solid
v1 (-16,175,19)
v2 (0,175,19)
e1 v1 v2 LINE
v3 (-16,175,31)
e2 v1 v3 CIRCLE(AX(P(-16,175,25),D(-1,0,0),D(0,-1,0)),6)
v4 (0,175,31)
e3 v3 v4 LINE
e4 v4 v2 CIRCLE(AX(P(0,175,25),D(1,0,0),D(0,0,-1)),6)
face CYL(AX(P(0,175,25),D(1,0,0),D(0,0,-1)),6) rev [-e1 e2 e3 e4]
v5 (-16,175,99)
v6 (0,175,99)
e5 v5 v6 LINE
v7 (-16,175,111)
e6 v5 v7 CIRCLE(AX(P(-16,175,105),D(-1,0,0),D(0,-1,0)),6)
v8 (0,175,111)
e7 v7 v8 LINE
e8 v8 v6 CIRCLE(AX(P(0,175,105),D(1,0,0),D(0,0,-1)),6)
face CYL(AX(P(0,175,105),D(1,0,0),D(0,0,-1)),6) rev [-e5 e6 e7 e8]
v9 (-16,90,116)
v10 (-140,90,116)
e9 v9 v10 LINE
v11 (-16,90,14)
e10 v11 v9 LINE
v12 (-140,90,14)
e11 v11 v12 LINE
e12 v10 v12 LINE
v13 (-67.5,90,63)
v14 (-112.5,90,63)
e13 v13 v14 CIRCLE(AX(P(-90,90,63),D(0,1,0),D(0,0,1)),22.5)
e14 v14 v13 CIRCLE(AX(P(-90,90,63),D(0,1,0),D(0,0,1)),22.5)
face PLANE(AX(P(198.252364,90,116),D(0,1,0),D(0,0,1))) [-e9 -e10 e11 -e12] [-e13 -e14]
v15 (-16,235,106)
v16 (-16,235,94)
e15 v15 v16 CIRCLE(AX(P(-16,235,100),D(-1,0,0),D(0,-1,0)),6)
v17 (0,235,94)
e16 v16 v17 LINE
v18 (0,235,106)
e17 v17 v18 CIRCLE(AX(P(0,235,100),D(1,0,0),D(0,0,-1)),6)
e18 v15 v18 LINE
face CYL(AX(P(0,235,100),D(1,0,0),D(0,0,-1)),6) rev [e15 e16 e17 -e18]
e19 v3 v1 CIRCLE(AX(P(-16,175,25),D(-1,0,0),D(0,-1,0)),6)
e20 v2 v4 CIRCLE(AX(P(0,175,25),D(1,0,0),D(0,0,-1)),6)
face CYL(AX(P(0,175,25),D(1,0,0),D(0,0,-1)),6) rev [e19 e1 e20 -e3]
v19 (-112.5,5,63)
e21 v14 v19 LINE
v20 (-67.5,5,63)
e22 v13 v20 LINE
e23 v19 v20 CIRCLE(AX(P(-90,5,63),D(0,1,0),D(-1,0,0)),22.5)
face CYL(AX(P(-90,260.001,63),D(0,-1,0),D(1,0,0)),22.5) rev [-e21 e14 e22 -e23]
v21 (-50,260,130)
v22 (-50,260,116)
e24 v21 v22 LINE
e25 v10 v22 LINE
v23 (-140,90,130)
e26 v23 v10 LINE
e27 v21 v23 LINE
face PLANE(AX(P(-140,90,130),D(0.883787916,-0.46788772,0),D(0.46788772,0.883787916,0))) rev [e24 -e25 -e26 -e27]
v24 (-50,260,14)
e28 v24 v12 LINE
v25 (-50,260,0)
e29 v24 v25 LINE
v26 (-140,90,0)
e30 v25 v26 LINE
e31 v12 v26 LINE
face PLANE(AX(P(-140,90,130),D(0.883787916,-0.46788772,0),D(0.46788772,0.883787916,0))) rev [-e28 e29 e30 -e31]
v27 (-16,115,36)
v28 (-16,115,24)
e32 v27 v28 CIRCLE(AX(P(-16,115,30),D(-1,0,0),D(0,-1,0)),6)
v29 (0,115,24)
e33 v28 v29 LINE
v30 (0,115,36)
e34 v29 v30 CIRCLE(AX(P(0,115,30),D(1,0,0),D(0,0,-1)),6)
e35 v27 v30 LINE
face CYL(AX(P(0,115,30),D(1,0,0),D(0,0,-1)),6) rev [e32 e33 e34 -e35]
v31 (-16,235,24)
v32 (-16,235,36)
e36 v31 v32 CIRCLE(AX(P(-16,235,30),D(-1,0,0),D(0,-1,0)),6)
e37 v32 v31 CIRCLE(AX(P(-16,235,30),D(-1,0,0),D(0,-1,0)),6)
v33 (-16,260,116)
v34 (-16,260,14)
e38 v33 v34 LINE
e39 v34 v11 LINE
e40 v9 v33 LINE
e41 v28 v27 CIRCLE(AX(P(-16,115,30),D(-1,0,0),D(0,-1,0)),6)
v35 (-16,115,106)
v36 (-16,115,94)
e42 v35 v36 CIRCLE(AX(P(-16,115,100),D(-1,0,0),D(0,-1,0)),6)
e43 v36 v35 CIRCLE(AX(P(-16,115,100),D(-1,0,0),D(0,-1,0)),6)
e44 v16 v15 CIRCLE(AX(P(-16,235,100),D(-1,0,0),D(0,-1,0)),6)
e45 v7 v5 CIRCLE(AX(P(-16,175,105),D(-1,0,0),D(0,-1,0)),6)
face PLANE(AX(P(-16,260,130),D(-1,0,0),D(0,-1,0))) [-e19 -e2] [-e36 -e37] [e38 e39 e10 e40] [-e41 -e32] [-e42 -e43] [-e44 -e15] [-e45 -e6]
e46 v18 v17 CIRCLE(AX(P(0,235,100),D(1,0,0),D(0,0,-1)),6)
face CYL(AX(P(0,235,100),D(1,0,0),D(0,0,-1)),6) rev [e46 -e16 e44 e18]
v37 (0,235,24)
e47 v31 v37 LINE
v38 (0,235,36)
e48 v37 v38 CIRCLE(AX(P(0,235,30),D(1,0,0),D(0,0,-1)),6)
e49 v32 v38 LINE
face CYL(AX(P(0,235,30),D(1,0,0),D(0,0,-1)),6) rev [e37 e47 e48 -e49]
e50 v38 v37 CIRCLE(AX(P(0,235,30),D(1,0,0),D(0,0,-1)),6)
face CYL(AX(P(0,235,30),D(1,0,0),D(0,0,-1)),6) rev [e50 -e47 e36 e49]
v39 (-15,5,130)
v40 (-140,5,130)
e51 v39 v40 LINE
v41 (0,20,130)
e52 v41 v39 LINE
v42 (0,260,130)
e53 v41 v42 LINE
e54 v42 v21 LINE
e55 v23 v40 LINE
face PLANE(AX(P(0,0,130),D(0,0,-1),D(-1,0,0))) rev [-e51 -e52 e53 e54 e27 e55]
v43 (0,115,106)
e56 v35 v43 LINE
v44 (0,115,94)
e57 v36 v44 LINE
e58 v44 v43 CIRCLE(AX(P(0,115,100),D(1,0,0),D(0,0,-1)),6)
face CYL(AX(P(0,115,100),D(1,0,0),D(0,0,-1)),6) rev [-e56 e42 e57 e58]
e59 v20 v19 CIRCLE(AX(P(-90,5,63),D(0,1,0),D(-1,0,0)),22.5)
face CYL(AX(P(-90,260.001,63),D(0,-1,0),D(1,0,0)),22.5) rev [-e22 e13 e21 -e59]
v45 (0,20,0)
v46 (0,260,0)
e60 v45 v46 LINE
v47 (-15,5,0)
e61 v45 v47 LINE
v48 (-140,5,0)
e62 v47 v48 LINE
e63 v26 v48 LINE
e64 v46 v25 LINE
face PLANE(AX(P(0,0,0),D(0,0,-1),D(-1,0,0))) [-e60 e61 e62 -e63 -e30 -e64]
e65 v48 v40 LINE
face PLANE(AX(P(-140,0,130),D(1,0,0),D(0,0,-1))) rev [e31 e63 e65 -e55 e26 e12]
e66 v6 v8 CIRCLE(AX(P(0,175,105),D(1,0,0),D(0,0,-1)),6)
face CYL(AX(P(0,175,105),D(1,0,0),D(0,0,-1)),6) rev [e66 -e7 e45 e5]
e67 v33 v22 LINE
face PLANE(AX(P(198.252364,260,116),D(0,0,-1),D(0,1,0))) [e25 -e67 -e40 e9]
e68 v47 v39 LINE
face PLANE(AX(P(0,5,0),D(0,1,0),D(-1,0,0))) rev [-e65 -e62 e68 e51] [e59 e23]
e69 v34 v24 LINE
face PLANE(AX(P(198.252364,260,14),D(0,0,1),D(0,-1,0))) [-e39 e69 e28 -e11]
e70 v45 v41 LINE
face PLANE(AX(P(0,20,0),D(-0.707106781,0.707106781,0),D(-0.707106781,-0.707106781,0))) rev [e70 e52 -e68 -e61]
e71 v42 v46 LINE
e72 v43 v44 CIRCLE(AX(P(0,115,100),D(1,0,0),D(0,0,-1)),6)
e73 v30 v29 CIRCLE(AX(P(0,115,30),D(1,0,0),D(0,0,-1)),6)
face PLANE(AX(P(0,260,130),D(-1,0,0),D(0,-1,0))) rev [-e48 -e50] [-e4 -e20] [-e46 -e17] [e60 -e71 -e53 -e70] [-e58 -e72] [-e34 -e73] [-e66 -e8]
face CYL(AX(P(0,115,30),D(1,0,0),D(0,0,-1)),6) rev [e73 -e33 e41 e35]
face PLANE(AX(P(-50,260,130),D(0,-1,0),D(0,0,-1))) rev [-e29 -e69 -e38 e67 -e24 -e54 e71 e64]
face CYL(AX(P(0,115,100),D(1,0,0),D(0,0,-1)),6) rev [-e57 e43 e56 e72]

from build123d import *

# Parameters (mm, degrees)
EXTRUDE_1_DEPTH             = 130
SKETCH_2_W                  = 140
SKETCH_2_H                  = 5
CUT_EXTRUDE_1_DEPTH         = 323.645316098
SKETCH_3_W                  = 102
SKETCH_3_H                  = 170
CUT_EXTRUDE_2_DEPTH         = 124
CUT_EXTRUDE_3_DEPTH         = 323.645316098
HOLE_WIZARD_M14_1_D         = 12
HOLE_WIZARD_M14_1_DEPTH     = 34
HOLE_WIZARD_M14_1_TIP       = 3.605163714
HOLE_WIZARD_12_0_12_1_D     = 12
HOLE_WIZARD_12_0_12_1_DEPTH = 34
HOLE_WIZARD_12_0_12_1_TIP   = 3.605163714
CUT_EXTRUDE_4_REACH         = 302.299
SKETCH_12_R                 = 22.5


with BuildPart() as part:
    # 草图1 → 凸台-拉伸1 (new body)
    with BuildSketch(Plane.XY):
        Polygon((0, 0), (-140, 0), (-140, 90), (-50, 260), (0, 260), align=None)
    extrude(amount=EXTRUDE_1_DEPTH)

    # 草图2 → 切除-拉伸1 (cut, through all)
    with BuildSketch(Plane.XY.offset(130)):
        with Locations((-70, 2.5)):
            Rectangle(SKETCH_2_W, SKETCH_2_H)
    extrude(amount=-CUT_EXTRUDE_1_DEPTH, mode=Mode.SUBTRACT)

    # 草图3 → 切除-拉伸2 (cut)
    with BuildSketch(Plane(origin=(-140, 34.772640959, 0), x_dir=(0, 0, -1), z_dir=(1, 0, 0))):
        with Locations((-65, 140.227359041)):
            Rectangle(SKETCH_3_W, SKETCH_3_H)
    extrude(amount=CUT_EXTRUDE_2_DEPTH, mode=Mode.SUBTRACT)

    # 草图5 → 切除-拉伸3 (cut, through all)
    with BuildSketch(Plane.XY.offset(130)):
        Polygon((0, 5), (0, 20), (-15, 5), align=None)
    extrude(amount=-CUT_EXTRUDE_3_DEPTH, mode=Mode.SUBTRACT)

    # M14 螺纹孔1
    with Locations(Plane(origin=(0, 0, 0), x_dir=(0, 0, -1), z_dir=(1, 0, 0))):
        with Locations((-100, 235), (-30, 235), (-100, 115), (-30, 115)):
            Hole(HOLE_WIZARD_M14_1_D / 2, depth=HOLE_WIZARD_M14_1_DEPTH)
            with Locations((0, 0, -(HOLE_WIZARD_M14_1_DEPTH + HOLE_WIZARD_M14_1_TIP / 2))):  # 118° drill point
                Cone(0, HOLE_WIZARD_M14_1_D / 2, HOLE_WIZARD_M14_1_TIP, mode=Mode.SUBTRACT)

    # Ø12.0 (12) 直径孔1
    with Locations(Plane(origin=(0, 0, 0), x_dir=(0, 0, -1), z_dir=(1, 0, 0))):
        with Locations((-105, 175), (-25, 175)):
            Hole(HOLE_WIZARD_12_0_12_1_D / 2, depth=HOLE_WIZARD_12_0_12_1_DEPTH)
            with Locations((0, 0, -(HOLE_WIZARD_12_0_12_1_DEPTH + HOLE_WIZARD_12_0_12_1_TIP / 2))):  # 118° drill point
                Cone(0, HOLE_WIZARD_12_0_12_1_D / 2, HOLE_WIZARD_12_0_12_1_TIP, mode=Mode.SUBTRACT)

    # 草图12 → 切除-拉伸4 (cut, up to next)
    with BuildSketch(Plane(origin=(-90.854033512, 5, 0), x_dir=(-1, 0, 0), z_dir=(0, 1, 0)), mode=Mode.PRIVATE) as cut_extrude_4_sk1:
        with Locations(Location((-0.854033512, 63, 0), (0, 0, 90))):
            Circle(SKETCH_12_R)
    cut_extrude_4_tool1 = extrude(cut_extrude_4_sk1.sketch, amount=CUT_EXTRUDE_4_REACH, mode=Mode.PRIVATE) & part.part
    add(cut_extrude_4_tool1.solids().sort_by_distance((-90, 5, 63))[0], mode=Mode.SUBTRACT)


solid = part.part
